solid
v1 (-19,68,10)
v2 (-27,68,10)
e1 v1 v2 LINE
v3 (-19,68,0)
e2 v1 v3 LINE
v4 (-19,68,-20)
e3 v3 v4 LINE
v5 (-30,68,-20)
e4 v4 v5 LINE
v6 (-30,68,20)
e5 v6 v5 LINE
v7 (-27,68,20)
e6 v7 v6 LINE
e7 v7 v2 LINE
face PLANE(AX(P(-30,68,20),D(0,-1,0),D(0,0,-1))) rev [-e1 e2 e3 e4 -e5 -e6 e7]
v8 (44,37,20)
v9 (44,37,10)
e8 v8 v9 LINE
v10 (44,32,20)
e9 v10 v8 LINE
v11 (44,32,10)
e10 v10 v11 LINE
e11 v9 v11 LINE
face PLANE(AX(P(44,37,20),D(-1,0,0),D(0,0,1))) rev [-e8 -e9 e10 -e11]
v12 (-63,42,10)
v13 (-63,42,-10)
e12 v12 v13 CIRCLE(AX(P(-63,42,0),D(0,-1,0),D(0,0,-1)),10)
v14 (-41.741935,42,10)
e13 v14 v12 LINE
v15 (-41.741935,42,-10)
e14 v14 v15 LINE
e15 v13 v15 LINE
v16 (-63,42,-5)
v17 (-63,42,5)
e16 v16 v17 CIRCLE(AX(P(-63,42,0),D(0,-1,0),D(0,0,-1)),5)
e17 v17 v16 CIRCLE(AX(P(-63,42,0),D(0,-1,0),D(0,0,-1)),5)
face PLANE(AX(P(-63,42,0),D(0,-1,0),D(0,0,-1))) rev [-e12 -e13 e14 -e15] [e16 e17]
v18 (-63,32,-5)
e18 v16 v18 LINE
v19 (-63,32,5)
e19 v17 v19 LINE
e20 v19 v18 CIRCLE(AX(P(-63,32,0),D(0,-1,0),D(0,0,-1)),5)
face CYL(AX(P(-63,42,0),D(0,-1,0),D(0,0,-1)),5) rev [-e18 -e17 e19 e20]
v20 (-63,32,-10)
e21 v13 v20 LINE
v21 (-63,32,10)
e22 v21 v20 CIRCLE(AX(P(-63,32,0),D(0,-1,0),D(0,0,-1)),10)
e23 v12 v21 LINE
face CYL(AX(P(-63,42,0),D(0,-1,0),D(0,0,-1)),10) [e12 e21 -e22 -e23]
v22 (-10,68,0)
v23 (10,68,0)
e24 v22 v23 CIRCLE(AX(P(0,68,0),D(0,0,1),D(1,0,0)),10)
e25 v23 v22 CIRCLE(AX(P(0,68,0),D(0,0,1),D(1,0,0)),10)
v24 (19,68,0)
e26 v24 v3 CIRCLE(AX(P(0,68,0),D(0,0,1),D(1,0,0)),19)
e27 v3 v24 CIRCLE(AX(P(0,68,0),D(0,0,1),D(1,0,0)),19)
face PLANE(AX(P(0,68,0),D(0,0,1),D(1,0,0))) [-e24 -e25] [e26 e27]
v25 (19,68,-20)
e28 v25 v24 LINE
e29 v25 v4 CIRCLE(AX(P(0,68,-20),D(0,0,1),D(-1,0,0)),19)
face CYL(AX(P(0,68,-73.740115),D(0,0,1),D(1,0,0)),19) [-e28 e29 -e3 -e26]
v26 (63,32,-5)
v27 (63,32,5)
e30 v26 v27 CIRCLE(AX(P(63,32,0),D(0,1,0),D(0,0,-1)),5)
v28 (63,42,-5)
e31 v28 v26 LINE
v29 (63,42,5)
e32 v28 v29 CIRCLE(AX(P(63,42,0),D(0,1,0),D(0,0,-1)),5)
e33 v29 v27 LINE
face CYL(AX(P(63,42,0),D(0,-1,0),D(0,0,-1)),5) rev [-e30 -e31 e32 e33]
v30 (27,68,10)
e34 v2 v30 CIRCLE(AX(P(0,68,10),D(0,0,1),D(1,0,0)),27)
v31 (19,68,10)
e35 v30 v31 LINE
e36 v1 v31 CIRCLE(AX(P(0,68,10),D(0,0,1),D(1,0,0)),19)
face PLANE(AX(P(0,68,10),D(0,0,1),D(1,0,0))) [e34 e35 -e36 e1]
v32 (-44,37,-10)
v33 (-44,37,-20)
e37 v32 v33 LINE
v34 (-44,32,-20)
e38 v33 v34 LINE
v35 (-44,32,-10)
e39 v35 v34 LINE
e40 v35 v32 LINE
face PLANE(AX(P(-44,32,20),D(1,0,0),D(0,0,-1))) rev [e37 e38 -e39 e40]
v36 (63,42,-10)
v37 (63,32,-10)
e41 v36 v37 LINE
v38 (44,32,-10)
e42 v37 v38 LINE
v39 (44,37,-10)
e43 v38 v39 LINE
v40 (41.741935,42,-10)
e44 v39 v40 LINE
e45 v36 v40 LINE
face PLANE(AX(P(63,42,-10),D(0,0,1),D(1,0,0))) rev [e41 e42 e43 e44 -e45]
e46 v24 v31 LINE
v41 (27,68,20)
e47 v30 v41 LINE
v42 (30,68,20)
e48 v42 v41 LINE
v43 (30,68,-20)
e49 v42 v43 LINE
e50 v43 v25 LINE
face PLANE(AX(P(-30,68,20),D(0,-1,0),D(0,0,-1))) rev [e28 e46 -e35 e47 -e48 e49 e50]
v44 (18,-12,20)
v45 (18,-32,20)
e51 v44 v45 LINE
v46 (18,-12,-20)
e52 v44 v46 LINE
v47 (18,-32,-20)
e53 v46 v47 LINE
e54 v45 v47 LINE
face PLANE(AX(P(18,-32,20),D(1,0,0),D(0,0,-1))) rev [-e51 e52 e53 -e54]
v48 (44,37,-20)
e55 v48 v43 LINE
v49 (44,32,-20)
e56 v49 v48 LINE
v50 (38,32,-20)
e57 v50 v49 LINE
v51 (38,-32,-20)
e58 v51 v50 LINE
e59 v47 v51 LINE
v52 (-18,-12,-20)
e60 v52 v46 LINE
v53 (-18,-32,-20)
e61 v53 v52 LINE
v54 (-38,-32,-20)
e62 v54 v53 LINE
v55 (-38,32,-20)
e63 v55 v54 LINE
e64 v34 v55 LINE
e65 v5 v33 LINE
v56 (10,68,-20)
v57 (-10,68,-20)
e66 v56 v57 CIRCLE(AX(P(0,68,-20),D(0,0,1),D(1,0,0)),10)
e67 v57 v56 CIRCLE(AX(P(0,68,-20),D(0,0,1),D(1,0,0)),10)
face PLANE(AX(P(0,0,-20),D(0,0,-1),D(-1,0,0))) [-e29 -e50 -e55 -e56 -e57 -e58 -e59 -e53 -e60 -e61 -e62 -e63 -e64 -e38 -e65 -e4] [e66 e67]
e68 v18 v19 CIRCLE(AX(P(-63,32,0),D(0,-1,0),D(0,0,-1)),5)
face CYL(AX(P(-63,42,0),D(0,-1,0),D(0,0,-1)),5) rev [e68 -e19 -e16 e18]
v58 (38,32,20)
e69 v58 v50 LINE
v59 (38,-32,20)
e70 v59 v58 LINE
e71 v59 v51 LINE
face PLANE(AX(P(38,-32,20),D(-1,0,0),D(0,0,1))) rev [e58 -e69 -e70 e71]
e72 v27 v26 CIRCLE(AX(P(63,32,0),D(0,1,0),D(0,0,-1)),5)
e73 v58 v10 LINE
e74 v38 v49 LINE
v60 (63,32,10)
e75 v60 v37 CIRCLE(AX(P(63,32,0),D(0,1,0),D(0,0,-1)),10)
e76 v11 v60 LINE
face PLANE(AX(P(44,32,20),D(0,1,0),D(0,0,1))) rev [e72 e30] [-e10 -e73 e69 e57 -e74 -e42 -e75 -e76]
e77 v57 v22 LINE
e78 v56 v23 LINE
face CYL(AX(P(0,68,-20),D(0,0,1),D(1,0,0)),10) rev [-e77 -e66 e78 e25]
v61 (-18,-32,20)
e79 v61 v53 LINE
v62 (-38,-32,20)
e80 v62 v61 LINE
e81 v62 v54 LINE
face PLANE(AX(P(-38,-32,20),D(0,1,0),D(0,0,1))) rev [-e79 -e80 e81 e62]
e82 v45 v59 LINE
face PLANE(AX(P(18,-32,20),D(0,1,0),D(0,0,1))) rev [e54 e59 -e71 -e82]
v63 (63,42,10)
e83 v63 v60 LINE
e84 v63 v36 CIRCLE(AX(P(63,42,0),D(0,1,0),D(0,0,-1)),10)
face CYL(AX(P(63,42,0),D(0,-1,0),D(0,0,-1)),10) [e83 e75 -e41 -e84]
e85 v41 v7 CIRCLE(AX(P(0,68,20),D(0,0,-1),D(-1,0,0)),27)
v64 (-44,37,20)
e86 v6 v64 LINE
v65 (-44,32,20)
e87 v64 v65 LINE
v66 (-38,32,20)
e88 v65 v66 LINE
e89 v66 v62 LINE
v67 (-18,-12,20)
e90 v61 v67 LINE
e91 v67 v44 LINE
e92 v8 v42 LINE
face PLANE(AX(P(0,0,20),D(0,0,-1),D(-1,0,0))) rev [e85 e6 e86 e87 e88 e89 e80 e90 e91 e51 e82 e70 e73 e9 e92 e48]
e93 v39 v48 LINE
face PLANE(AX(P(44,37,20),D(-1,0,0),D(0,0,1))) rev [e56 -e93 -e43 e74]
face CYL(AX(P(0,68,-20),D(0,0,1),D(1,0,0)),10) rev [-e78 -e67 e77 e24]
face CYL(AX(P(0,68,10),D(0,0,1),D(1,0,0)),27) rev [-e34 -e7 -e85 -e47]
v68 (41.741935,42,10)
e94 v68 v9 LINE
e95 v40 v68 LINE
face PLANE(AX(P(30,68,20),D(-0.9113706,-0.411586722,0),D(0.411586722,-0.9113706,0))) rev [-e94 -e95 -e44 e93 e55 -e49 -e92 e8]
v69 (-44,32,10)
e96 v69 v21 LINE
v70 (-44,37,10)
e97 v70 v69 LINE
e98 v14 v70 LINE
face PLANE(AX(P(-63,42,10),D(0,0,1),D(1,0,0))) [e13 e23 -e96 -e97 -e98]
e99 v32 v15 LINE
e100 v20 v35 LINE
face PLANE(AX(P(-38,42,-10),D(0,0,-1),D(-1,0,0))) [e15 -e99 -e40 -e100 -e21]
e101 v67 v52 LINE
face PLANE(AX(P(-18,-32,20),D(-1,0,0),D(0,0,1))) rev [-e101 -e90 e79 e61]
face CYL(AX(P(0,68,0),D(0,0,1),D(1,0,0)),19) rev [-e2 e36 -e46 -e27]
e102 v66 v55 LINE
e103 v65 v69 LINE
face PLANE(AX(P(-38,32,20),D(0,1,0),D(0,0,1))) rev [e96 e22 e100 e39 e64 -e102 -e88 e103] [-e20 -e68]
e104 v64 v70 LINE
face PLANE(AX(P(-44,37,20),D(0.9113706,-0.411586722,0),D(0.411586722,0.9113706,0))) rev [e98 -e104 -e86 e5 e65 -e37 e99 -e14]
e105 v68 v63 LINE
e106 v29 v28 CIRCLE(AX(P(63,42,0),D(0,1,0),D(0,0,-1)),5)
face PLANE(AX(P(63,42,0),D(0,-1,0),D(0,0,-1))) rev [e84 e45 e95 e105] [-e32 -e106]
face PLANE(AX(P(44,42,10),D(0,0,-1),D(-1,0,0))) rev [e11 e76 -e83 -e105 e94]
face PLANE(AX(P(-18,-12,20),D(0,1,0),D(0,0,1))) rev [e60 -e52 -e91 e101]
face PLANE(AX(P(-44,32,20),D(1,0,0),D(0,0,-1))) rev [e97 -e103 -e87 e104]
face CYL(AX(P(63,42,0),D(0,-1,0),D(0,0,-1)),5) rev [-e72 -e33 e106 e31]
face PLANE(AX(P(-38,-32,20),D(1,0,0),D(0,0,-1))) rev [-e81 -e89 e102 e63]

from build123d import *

# Parameters (mm, degrees)
PEDESTAL_BODY_DEPTH      = 20
FRONT_RECESS_54_SKETCH_R = 27
FRONT_RECESS_54_DEPTH    = 10
INNER_RECESS_38_SKETCH_R = 19
INNER_RECESS_38_DEPTH    = 10
HUB_38_SKETCH_R          = 19
HUB_38_DEPTH             = 20
BORE_20_SKETCH_R         = 10
BORE_20_DEPTH            = 100.523866484
MOUNTING_EAR_SKETCH_R    = 5
MOUNTING_EAR_DEPTH       = 10


with BuildPart() as part:
    # Pedestal Profile Sketch → Pedestal Body (new, symmetric)
    with BuildSketch(Plane.XY):
        Polygon((18, -32), (38, -32), (38, 32), (44, 32), (44, 37), (30, 68), (-30, 68), (-44, 37), (-44, 32), (-38, 32), (-38, -32), (-18, -32), (-18, -12), (18, -12), align=None)
    extrude(amount=PEDESTAL_BODY_DEPTH, both=True)

    # Front Recess Ø54 Sketch → Front Recess Ø54 (cut)
    with BuildSketch(Plane.XY.offset(20)):
        with Locations((0, 68)):
            Circle(FRONT_RECESS_54_SKETCH_R)
    extrude(amount=-FRONT_RECESS_54_DEPTH, mode=Mode.SUBTRACT)

    # Inner Recess Ø38 Sketch → Inner Recess Ø38 (cut)
    with BuildSketch(Plane.XY.offset(10)):
        with Locations((0, 68)):
            Circle(INNER_RECESS_38_SKETCH_R)
    extrude(amount=-INNER_RECESS_38_DEPTH, mode=Mode.SUBTRACT)

    # Hub Ø38 Sketch → Hub Ø38 (add)
    with BuildSketch(Plane.XY):
        with Locations((0, 68)):
            Circle(HUB_38_SKETCH_R)
    extrude(amount=-HUB_38_DEPTH)

    # Bore Ø20 Sketch → Bore Ø20 (cut, through all)
    with BuildSketch(Plane.XY):
        with Locations((0, 68)):
            Circle(BORE_20_SKETCH_R)
    extrude(amount=-BORE_20_DEPTH, mode=Mode.SUBTRACT)

    # Mounting Ear Sketch → Mounting Ear (add)
    with BuildSketch(Plane.XZ.offset(-32)):
        with BuildLine():
            Line((-63, 10), (-44, 10))
            Line((-44, 10), (-38, 10))
            Line((-38, 10), (-38, -10))
            Line((-38, -10), (-44, -10))
            Line((-44, -10), (-63, -10))
            ThreePointArc((-63, -10), (-73, 0), (-63, 10))
        make_face()
        with Locations(Location((-63, 0, 0), (0, 0, 270))):
            Circle(MOUNTING_EAR_SKETCH_R, mode=Mode.SUBTRACT)
    mounting_ear = extrude(amount=-MOUNTING_EAR_DEPTH)

    # Mounting Ear Mirror: Mounting Ear across plane
    add(mounting_ear.mirror(Plane(origin=(0, 0, 0), x_dir=(0, 0, 1), z_dir=(1, 0, 0))))


solid = part.part
